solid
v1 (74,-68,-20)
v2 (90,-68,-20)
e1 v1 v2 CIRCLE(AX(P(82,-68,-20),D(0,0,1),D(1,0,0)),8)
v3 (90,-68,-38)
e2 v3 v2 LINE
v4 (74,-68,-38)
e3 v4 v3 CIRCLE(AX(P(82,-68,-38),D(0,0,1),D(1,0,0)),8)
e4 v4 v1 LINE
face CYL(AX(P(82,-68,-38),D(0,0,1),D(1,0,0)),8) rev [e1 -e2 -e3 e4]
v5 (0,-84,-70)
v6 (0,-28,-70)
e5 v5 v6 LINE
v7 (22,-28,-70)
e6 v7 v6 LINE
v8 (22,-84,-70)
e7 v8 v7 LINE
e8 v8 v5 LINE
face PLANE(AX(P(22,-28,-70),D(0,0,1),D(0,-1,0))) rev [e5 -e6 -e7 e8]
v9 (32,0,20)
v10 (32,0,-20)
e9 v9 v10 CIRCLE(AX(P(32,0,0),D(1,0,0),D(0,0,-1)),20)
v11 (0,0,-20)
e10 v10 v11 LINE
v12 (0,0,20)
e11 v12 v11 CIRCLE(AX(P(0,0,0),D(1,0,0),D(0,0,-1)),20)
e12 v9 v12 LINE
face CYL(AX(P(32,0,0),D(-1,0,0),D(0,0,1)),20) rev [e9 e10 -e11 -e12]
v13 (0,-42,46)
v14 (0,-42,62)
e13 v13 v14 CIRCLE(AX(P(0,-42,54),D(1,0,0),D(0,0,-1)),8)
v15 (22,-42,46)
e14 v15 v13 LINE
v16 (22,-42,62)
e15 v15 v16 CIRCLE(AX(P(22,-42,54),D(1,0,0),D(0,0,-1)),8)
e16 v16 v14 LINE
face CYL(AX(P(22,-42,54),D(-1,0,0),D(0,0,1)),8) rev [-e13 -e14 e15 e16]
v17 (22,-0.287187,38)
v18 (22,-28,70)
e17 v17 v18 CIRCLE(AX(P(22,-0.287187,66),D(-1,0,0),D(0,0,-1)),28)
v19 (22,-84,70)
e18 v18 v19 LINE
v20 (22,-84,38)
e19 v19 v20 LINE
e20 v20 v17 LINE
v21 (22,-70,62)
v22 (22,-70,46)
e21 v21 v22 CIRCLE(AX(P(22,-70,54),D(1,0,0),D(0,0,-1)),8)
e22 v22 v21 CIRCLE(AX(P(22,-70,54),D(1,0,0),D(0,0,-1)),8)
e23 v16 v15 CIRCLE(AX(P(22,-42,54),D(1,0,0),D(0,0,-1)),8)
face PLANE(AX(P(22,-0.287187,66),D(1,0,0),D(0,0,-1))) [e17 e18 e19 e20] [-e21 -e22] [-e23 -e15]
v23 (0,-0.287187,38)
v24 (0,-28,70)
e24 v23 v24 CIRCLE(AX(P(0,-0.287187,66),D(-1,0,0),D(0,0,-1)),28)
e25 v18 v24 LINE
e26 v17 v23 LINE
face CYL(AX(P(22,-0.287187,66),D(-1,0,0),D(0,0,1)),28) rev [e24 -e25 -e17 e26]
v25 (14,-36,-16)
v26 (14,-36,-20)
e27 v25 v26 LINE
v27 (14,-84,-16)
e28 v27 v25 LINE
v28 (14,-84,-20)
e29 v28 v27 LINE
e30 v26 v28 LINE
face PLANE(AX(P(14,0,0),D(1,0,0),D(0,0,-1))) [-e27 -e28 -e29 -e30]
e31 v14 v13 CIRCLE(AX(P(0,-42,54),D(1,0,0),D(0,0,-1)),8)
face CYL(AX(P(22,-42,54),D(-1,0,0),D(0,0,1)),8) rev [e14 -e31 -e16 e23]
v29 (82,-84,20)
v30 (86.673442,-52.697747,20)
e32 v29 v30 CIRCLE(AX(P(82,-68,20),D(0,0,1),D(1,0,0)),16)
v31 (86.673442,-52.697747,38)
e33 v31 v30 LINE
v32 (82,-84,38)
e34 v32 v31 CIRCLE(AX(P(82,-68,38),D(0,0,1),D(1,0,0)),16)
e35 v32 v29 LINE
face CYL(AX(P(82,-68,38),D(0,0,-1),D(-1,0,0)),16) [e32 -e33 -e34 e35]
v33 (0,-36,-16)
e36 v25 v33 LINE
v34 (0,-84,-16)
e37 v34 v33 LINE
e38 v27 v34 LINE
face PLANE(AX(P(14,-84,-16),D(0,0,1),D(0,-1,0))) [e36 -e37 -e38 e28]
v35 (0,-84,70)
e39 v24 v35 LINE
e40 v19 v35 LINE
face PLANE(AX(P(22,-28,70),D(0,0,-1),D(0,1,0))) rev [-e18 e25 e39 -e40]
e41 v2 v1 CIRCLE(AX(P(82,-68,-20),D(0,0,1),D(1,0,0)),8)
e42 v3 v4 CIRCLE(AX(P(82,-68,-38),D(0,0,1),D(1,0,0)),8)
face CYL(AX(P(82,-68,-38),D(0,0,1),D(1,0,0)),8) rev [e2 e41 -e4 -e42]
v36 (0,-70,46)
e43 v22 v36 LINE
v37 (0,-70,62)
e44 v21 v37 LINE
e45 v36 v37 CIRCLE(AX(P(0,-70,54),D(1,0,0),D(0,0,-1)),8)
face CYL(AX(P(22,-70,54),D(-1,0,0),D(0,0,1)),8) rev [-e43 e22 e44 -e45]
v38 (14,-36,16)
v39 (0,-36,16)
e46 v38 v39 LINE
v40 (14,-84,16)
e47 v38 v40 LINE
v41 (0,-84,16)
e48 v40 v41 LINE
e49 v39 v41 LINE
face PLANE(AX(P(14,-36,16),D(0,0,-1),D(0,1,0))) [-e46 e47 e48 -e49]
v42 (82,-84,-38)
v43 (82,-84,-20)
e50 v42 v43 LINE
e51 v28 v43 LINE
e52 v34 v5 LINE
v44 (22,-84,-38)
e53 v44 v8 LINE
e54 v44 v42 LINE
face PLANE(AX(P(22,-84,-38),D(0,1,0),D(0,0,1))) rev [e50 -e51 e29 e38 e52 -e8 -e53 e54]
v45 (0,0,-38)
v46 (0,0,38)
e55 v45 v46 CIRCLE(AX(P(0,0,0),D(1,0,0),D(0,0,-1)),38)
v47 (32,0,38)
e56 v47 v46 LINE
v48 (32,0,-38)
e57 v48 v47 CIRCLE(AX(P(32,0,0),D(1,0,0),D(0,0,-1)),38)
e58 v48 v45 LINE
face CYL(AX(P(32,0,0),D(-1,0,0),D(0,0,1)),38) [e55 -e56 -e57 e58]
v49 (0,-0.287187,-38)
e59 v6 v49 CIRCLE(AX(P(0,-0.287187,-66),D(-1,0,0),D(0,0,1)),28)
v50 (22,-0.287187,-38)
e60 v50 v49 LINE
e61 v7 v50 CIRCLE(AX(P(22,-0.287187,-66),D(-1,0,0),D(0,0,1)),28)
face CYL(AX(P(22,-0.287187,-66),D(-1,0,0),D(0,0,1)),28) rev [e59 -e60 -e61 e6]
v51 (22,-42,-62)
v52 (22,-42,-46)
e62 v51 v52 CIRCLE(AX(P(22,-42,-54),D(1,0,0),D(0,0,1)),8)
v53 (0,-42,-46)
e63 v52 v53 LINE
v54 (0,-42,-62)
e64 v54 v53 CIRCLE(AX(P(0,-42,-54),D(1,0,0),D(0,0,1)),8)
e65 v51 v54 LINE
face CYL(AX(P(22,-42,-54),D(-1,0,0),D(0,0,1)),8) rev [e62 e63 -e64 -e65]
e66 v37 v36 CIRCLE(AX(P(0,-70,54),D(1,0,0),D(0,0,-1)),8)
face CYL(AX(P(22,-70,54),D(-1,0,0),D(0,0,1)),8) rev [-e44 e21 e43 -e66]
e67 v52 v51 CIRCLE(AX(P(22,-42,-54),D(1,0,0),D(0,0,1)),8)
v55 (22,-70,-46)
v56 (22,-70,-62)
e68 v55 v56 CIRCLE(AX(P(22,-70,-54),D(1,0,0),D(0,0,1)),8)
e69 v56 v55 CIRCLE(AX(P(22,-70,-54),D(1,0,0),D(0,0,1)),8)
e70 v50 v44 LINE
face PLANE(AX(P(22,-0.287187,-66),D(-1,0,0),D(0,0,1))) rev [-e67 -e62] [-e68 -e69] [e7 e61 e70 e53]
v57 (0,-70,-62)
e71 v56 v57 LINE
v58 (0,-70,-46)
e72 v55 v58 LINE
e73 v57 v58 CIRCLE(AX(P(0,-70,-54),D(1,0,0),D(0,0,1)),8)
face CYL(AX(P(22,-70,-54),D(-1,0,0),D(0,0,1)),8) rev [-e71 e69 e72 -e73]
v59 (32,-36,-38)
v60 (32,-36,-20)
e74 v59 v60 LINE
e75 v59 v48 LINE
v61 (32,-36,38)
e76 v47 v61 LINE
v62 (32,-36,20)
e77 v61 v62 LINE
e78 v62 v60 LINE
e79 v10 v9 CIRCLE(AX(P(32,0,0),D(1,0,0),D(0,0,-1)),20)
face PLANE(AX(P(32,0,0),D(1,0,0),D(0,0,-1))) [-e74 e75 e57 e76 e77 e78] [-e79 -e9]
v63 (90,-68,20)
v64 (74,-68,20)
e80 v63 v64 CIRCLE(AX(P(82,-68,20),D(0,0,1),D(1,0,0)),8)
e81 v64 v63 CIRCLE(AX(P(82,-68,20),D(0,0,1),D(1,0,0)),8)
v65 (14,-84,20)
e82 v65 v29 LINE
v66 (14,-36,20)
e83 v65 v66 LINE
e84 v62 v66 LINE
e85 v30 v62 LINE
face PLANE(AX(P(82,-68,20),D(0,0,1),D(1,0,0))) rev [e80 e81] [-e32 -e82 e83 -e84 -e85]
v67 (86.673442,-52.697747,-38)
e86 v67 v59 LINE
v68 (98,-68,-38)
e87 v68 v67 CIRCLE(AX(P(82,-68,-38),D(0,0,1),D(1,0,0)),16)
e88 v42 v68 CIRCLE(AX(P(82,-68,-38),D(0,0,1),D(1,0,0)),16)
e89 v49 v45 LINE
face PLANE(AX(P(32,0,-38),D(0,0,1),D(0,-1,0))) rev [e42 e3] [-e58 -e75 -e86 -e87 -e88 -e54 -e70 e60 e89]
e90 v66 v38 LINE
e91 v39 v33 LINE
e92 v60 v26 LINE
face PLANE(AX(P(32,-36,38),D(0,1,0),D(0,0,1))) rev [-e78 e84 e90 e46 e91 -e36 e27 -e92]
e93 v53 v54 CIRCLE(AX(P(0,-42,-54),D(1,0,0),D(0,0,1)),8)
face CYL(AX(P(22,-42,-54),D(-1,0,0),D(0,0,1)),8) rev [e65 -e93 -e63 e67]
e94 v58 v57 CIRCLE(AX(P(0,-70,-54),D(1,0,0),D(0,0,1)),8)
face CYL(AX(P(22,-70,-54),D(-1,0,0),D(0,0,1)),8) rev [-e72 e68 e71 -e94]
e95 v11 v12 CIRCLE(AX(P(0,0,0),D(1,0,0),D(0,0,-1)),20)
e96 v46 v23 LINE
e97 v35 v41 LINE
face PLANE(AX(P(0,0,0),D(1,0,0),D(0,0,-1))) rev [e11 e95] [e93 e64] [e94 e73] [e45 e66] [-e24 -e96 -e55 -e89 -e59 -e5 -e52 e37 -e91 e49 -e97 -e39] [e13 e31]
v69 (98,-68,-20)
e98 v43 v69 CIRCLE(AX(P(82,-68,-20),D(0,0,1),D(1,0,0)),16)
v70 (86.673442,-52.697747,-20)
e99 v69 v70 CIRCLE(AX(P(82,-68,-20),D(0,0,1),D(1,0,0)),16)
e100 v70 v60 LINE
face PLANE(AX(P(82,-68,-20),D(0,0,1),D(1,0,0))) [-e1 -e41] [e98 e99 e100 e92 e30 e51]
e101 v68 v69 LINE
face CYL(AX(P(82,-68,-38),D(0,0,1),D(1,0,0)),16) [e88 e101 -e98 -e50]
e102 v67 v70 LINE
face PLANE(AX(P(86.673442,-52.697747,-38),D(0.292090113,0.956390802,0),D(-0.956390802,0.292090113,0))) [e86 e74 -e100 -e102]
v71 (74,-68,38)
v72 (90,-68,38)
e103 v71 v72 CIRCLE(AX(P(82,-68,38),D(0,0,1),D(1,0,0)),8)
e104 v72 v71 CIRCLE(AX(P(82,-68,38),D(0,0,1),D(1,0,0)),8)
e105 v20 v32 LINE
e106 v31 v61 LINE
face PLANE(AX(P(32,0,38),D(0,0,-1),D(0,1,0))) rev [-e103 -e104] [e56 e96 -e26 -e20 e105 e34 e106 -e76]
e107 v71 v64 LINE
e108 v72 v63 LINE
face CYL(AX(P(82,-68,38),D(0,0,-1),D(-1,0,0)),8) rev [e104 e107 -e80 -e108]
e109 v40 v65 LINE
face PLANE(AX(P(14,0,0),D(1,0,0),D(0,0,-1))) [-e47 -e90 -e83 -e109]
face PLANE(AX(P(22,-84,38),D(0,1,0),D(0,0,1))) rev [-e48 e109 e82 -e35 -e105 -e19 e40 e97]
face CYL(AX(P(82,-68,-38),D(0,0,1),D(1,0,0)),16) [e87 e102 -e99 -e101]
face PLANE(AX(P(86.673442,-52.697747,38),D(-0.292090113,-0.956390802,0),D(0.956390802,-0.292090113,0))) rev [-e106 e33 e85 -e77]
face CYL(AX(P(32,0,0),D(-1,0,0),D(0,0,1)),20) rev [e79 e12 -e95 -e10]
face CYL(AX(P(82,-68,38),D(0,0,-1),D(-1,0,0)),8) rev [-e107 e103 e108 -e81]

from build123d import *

# Parameters (mm, degrees)
BASE_BLOCK_SKETCH_R  = 20
BASE_BLOCK_DEPTH     = 32
PIVOT_BOSS_SKETCH_R  = 8
PIVOT_BOSS_DEPTH     = 22
ARM_START            = 20
ARM_PROFILE_SKETCH_R = 8
ARM_1_DEPTH          = 18
ARM_START_2          = -38
SKETCH3_2_R          = 8
ARM_2_DEPTH          = 18
SIDE_LUG_SKETCH_W    = 4
SIDE_LUG_SKETCH_H    = 48
SIDE_LUGS_DEPTH      = 14


with BuildPart() as part:
    # Base Block Sketch → Base Block (new body)
    with BuildSketch(Plane(origin=(0, 0, 0), x_dir=(0, 0, -1), z_dir=(1, 0, 0))):
        with BuildLine():
            Line((-38, 0), (-38, -36))
            Line((-38, -36), (38, -36))
            Line((38, -36), (38, 0))
            ThreePointArc((38, 0), (0, 38), (-38, 0))
        make_face()
        Circle(BASE_BLOCK_SKETCH_R, mode=Mode.SUBTRACT)
    extrude(amount=BASE_BLOCK_DEPTH)

    # Pivot Boss Sketch → Pivot Boss (add)
    # profile 1 of 2: a face of its own
    with BuildSketch(Plane(origin=(0, 0, 0), x_dir=(0, 0, -1), z_dir=(1, 0, 0))):
        with BuildLine():
            Line((-38, -0.287187079), (-38, -84))
            Line((-38, -84), (-70, -84))
            Line((-70, -84), (-70, -28))
            ThreePointArc((-70, -28), (-47.66969722, -21.453197567), (-38, -0.287187079))
        make_face()
        with Locations((-54, -42)):
            Circle(PIVOT_BOSS_SKETCH_R, mode=Mode.SUBTRACT)
        with Locations((-54, -70)):
            Circle(PIVOT_BOSS_SKETCH_R, mode=Mode.SUBTRACT)
    # profile 2 of 2: a face of its own
    with BuildSketch(Plane(origin=(0, 0, 0), x_dir=(0, 0, -1), z_dir=(1, 0, 0))):
        with BuildLine():
            Line((70, -28), (70, -84))
            Line((70, -84), (38, -84))
            Line((38, -84), (38, -0.287187079))
            ThreePointArc((38, -0.287187079), (47.66969722, -21.453197567), (70, -28))
        make_face()
        with Locations(Location((54, -70, 0), (0, 0, 180))):
            Circle(PIVOT_BOSS_SKETCH_R, mode=Mode.SUBTRACT)
        with Locations(Location((54, -42, 0), (0, 0, 180))):
            Circle(PIVOT_BOSS_SKETCH_R, mode=Mode.SUBTRACT)
    extrude(amount=PIVOT_BOSS_DEPTH)

    # Arm Profile Sketch → Arm 1 (add)
    with BuildSketch(Plane.XY.offset(ARM_START)):
        with BuildLine():
            Line((0, -84), (82, -84))
            ThreePointArc((82, -84), (97.824601816, -70.362620868), (86.673441811, -52.697747171))
            Line((86.673441811, -52.697747171), (32, -36))
            Line((32, -36), (0, -36))
            Line((0, -36), (0, -84))
        make_face()
        with Locations((82, -68)):
            Circle(ARM_PROFILE_SKETCH_R, mode=Mode.SUBTRACT)
    extrude(amount=ARM_1_DEPTH)

    # Sketch3_2 → Arm 2 (add)
    with BuildSketch(Plane.XY.offset(ARM_START_2)):
        with BuildLine():
            Line((0, -84), (82, -84))
            ThreePointArc((82, -84), (97.824601816, -70.362620868), (86.673441811, -52.697747171))
            Line((86.673441811, -52.697747171), (32, -36))
            Line((32, -36), (0, -36))
            Line((0, -36), (0, -84))
        make_face()
        with Locations((82, -68)):
            Circle(SKETCH3_2_R, mode=Mode.SUBTRACT)
    extrude(amount=ARM_2_DEPTH)

    # Side Lug Sketch → Side Lugs (add)
    with BuildSketch(Plane.ZY):
        with Locations((-18, -60)):
            Rectangle(SIDE_LUG_SKETCH_W, SIDE_LUG_SKETCH_H)
        with Locations((18, -60)):
            Rectangle(SIDE_LUG_SKETCH_W, SIDE_LUG_SKETCH_H)
    extrude(amount=-SIDE_LUGS_DEPTH)


solid = part.part
